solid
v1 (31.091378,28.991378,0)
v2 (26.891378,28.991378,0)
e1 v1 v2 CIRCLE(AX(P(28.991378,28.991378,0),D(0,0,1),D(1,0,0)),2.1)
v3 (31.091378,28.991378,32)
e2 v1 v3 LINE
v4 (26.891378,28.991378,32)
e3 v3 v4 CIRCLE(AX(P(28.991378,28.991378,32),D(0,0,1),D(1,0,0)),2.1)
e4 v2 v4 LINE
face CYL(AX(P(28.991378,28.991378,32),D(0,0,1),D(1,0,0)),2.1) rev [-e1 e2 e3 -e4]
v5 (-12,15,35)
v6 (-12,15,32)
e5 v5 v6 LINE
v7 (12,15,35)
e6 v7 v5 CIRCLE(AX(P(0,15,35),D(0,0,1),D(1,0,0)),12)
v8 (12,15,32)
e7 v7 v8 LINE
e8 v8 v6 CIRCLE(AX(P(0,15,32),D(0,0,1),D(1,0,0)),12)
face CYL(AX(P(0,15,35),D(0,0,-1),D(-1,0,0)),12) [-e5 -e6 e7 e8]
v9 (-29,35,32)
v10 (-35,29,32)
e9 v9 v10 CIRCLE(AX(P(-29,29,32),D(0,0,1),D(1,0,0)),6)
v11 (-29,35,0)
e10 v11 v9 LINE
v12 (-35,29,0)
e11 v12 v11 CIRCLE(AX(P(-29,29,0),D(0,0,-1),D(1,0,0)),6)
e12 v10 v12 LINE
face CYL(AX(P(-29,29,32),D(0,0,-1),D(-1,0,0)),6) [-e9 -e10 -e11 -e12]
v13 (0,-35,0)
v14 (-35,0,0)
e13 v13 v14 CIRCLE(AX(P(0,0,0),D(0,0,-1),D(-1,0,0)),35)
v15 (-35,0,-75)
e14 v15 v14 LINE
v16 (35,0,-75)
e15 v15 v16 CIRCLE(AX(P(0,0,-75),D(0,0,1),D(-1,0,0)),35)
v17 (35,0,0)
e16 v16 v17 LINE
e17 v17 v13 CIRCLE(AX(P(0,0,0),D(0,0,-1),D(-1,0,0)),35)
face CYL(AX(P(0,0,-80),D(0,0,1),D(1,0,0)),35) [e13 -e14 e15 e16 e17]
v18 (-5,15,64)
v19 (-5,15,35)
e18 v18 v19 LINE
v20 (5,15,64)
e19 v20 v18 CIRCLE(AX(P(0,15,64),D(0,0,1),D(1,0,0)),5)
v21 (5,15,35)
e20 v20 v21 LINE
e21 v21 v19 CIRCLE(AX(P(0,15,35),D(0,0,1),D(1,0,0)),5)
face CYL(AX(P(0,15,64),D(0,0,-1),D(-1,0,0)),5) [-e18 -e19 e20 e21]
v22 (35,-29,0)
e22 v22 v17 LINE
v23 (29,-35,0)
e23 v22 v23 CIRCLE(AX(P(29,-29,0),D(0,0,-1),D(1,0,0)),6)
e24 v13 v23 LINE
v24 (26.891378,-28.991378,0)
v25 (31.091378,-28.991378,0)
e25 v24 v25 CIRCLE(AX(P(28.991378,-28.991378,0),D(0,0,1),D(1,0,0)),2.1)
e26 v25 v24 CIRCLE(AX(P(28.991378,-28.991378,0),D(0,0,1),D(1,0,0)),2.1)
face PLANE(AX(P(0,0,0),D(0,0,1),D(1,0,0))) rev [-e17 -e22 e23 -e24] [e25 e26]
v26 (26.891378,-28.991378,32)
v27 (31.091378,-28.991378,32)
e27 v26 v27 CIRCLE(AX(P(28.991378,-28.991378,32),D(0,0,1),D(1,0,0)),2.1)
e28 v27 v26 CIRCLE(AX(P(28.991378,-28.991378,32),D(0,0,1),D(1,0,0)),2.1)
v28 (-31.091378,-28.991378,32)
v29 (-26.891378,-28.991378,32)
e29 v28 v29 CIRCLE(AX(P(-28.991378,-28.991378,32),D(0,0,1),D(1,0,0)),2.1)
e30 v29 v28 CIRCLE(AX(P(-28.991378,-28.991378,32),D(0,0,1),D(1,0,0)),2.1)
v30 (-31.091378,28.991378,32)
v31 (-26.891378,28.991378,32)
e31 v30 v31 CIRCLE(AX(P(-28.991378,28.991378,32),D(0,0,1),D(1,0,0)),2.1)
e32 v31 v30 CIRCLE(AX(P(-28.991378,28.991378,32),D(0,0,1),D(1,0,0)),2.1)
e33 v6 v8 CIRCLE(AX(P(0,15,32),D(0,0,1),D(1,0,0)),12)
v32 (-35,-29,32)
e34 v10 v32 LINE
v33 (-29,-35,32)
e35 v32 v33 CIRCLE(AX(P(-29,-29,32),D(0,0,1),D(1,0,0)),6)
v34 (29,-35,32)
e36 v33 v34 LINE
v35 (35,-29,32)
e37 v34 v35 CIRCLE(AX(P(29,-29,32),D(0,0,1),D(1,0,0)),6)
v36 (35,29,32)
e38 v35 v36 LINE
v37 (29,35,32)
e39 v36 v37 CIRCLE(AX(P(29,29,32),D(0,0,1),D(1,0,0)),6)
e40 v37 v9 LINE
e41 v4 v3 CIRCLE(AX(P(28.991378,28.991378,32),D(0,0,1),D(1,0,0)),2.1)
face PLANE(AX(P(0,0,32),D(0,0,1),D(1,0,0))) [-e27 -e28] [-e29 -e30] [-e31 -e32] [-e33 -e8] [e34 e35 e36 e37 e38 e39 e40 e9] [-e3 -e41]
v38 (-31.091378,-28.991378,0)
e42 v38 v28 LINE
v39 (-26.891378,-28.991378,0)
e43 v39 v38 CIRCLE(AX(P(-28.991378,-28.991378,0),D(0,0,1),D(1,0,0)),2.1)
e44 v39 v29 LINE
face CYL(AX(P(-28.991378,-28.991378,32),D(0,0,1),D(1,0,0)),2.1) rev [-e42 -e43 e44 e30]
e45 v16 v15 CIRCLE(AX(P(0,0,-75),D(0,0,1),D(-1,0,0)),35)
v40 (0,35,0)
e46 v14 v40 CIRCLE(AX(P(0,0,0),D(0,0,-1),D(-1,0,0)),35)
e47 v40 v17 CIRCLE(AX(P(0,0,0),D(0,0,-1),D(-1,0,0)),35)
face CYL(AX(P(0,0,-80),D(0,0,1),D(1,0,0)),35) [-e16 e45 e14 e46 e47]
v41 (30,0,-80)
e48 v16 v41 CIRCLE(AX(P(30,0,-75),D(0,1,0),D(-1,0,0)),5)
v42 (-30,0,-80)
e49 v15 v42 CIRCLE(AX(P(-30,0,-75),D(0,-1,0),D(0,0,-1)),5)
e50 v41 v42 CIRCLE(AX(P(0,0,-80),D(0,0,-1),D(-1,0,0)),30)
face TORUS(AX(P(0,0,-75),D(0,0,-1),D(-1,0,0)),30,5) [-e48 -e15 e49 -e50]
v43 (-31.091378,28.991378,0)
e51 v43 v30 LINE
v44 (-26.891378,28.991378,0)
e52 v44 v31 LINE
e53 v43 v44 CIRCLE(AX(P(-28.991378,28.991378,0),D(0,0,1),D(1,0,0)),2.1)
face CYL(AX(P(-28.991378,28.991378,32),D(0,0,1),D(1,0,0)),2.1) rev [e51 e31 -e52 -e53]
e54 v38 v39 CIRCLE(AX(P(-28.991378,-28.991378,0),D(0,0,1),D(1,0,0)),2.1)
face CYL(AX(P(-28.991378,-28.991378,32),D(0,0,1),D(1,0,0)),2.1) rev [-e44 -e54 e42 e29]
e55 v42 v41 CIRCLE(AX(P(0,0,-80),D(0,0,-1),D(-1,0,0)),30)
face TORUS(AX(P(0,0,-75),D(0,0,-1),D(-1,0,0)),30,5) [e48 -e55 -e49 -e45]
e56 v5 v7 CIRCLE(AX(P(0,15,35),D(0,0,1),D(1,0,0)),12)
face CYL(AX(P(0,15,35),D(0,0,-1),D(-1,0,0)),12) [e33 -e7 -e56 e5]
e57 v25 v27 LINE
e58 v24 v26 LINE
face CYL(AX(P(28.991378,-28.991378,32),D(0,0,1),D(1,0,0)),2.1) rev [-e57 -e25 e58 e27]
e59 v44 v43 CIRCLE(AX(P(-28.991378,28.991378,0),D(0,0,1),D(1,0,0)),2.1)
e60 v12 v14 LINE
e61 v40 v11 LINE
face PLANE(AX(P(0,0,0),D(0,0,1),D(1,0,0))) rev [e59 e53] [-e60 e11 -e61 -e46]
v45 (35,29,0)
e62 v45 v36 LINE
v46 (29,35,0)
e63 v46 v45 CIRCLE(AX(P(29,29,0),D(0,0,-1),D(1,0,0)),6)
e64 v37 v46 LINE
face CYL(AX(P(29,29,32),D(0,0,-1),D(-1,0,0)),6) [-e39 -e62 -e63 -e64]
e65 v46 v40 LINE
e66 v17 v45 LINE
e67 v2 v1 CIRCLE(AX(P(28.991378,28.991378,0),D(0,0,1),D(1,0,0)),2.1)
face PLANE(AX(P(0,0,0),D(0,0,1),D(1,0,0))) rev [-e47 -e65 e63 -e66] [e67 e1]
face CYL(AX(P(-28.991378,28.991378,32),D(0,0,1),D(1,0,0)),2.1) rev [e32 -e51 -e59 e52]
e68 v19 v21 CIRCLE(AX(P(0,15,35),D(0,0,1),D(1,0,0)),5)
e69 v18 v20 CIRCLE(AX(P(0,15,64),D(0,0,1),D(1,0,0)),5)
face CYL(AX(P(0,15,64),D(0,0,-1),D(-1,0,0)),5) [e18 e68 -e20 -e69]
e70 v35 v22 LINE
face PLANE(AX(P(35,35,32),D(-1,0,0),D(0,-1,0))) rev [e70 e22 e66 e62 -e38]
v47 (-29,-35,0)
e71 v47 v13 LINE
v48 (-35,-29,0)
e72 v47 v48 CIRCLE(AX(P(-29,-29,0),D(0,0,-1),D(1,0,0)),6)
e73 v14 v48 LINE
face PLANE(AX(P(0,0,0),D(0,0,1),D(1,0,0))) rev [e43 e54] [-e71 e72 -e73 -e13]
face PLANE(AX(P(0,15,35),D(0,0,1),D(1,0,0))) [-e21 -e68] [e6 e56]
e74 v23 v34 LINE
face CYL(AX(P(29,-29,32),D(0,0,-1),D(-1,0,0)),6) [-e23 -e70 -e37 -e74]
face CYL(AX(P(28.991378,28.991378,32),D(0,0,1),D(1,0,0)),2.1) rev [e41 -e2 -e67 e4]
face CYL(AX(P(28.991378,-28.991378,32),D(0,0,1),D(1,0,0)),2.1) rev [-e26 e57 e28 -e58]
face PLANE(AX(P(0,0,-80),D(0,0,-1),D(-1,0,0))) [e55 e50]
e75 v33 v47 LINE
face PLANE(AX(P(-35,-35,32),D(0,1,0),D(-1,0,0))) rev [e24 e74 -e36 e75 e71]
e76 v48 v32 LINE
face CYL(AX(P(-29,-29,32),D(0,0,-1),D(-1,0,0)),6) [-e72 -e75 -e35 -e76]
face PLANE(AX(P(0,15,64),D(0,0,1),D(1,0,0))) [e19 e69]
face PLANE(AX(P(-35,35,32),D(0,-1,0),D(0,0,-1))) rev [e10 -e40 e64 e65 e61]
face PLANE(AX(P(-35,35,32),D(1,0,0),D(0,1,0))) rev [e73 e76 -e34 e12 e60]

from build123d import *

# Parameters (mm, degrees)
SKETCH_1_W         = 70
SKETCH_1_H         = 70
EXTRUDE_1_DEPTH    = 32
SKETCH_2_R         = 35
EXTRUDE_2_DEPTH    = 80
FILLET_1_R         = 6
FILLET_2_R         = 5
SKETCH_3_R         = 5
EXTRUDE_3_DEPTH    = 32
HOLE_WIZARD_M5_1_D = 4.2
SKETCH_7_R         = 12
EXTRUDE_4_DEPTH    = 3


with BuildPart() as part:
    # 草图1 → 凸台-拉伸1 (new body)
    with BuildSketch(Plane.XY):
        Rectangle(SKETCH_1_W, SKETCH_1_H)
    extrude(amount=EXTRUDE_1_DEPTH)

    # 草图2 → 凸台-拉伸2 (add)
    with BuildSketch(Plane(origin=(0, 0, 0), x_dir=(-1, 0, 0), z_dir=(0, 0, -1))):
        Circle(SKETCH_2_R)
    extrude(amount=EXTRUDE_2_DEPTH)

    # 圆角1
    fillet_1_edges = [part.edges().sort_by_distance(p)[0] for p in [
        (35, -35, 16),
        (-35, -35, 16),
        (-35, 35, 16),
        (35, 35, 16),
    ]]
    fillet(fillet_1_edges, radius=FILLET_1_R)

    # 圆角2
    fillet_2_edges = [part.edges().sort_by_distance(p)[0] for p in [
        (35, 0, -80),
    ]]
    fillet(fillet_2_edges, radius=FILLET_2_R)

    # 草图3 → 凸台-拉伸3 (add)
    with BuildSketch(Plane.XY.offset(32)):
        with Locations((0, 15)):
            Circle(SKETCH_3_R)
    extrude(amount=EXTRUDE_3_DEPTH)

    # M5 螺纹孔1 (through all)
    with Locations(Plane.XY.offset(32)):
        with Locations((-28.991378029, 28.991378029), (-28.991378029, -28.991378029), (28.991378029, -28.991378029), (28.991378029, 28.991378029)):
            Hole(HOLE_WIZARD_M5_1_D / 2)

    # 草图7 → 凸台-拉伸4 (add)
    with BuildSketch(Plane.XY.offset(32)):
        with Locations((0, 15)):
            Circle(SKETCH_7_R)
    extrude(amount=EXTRUDE_4_DEPTH)


solid = part.part
